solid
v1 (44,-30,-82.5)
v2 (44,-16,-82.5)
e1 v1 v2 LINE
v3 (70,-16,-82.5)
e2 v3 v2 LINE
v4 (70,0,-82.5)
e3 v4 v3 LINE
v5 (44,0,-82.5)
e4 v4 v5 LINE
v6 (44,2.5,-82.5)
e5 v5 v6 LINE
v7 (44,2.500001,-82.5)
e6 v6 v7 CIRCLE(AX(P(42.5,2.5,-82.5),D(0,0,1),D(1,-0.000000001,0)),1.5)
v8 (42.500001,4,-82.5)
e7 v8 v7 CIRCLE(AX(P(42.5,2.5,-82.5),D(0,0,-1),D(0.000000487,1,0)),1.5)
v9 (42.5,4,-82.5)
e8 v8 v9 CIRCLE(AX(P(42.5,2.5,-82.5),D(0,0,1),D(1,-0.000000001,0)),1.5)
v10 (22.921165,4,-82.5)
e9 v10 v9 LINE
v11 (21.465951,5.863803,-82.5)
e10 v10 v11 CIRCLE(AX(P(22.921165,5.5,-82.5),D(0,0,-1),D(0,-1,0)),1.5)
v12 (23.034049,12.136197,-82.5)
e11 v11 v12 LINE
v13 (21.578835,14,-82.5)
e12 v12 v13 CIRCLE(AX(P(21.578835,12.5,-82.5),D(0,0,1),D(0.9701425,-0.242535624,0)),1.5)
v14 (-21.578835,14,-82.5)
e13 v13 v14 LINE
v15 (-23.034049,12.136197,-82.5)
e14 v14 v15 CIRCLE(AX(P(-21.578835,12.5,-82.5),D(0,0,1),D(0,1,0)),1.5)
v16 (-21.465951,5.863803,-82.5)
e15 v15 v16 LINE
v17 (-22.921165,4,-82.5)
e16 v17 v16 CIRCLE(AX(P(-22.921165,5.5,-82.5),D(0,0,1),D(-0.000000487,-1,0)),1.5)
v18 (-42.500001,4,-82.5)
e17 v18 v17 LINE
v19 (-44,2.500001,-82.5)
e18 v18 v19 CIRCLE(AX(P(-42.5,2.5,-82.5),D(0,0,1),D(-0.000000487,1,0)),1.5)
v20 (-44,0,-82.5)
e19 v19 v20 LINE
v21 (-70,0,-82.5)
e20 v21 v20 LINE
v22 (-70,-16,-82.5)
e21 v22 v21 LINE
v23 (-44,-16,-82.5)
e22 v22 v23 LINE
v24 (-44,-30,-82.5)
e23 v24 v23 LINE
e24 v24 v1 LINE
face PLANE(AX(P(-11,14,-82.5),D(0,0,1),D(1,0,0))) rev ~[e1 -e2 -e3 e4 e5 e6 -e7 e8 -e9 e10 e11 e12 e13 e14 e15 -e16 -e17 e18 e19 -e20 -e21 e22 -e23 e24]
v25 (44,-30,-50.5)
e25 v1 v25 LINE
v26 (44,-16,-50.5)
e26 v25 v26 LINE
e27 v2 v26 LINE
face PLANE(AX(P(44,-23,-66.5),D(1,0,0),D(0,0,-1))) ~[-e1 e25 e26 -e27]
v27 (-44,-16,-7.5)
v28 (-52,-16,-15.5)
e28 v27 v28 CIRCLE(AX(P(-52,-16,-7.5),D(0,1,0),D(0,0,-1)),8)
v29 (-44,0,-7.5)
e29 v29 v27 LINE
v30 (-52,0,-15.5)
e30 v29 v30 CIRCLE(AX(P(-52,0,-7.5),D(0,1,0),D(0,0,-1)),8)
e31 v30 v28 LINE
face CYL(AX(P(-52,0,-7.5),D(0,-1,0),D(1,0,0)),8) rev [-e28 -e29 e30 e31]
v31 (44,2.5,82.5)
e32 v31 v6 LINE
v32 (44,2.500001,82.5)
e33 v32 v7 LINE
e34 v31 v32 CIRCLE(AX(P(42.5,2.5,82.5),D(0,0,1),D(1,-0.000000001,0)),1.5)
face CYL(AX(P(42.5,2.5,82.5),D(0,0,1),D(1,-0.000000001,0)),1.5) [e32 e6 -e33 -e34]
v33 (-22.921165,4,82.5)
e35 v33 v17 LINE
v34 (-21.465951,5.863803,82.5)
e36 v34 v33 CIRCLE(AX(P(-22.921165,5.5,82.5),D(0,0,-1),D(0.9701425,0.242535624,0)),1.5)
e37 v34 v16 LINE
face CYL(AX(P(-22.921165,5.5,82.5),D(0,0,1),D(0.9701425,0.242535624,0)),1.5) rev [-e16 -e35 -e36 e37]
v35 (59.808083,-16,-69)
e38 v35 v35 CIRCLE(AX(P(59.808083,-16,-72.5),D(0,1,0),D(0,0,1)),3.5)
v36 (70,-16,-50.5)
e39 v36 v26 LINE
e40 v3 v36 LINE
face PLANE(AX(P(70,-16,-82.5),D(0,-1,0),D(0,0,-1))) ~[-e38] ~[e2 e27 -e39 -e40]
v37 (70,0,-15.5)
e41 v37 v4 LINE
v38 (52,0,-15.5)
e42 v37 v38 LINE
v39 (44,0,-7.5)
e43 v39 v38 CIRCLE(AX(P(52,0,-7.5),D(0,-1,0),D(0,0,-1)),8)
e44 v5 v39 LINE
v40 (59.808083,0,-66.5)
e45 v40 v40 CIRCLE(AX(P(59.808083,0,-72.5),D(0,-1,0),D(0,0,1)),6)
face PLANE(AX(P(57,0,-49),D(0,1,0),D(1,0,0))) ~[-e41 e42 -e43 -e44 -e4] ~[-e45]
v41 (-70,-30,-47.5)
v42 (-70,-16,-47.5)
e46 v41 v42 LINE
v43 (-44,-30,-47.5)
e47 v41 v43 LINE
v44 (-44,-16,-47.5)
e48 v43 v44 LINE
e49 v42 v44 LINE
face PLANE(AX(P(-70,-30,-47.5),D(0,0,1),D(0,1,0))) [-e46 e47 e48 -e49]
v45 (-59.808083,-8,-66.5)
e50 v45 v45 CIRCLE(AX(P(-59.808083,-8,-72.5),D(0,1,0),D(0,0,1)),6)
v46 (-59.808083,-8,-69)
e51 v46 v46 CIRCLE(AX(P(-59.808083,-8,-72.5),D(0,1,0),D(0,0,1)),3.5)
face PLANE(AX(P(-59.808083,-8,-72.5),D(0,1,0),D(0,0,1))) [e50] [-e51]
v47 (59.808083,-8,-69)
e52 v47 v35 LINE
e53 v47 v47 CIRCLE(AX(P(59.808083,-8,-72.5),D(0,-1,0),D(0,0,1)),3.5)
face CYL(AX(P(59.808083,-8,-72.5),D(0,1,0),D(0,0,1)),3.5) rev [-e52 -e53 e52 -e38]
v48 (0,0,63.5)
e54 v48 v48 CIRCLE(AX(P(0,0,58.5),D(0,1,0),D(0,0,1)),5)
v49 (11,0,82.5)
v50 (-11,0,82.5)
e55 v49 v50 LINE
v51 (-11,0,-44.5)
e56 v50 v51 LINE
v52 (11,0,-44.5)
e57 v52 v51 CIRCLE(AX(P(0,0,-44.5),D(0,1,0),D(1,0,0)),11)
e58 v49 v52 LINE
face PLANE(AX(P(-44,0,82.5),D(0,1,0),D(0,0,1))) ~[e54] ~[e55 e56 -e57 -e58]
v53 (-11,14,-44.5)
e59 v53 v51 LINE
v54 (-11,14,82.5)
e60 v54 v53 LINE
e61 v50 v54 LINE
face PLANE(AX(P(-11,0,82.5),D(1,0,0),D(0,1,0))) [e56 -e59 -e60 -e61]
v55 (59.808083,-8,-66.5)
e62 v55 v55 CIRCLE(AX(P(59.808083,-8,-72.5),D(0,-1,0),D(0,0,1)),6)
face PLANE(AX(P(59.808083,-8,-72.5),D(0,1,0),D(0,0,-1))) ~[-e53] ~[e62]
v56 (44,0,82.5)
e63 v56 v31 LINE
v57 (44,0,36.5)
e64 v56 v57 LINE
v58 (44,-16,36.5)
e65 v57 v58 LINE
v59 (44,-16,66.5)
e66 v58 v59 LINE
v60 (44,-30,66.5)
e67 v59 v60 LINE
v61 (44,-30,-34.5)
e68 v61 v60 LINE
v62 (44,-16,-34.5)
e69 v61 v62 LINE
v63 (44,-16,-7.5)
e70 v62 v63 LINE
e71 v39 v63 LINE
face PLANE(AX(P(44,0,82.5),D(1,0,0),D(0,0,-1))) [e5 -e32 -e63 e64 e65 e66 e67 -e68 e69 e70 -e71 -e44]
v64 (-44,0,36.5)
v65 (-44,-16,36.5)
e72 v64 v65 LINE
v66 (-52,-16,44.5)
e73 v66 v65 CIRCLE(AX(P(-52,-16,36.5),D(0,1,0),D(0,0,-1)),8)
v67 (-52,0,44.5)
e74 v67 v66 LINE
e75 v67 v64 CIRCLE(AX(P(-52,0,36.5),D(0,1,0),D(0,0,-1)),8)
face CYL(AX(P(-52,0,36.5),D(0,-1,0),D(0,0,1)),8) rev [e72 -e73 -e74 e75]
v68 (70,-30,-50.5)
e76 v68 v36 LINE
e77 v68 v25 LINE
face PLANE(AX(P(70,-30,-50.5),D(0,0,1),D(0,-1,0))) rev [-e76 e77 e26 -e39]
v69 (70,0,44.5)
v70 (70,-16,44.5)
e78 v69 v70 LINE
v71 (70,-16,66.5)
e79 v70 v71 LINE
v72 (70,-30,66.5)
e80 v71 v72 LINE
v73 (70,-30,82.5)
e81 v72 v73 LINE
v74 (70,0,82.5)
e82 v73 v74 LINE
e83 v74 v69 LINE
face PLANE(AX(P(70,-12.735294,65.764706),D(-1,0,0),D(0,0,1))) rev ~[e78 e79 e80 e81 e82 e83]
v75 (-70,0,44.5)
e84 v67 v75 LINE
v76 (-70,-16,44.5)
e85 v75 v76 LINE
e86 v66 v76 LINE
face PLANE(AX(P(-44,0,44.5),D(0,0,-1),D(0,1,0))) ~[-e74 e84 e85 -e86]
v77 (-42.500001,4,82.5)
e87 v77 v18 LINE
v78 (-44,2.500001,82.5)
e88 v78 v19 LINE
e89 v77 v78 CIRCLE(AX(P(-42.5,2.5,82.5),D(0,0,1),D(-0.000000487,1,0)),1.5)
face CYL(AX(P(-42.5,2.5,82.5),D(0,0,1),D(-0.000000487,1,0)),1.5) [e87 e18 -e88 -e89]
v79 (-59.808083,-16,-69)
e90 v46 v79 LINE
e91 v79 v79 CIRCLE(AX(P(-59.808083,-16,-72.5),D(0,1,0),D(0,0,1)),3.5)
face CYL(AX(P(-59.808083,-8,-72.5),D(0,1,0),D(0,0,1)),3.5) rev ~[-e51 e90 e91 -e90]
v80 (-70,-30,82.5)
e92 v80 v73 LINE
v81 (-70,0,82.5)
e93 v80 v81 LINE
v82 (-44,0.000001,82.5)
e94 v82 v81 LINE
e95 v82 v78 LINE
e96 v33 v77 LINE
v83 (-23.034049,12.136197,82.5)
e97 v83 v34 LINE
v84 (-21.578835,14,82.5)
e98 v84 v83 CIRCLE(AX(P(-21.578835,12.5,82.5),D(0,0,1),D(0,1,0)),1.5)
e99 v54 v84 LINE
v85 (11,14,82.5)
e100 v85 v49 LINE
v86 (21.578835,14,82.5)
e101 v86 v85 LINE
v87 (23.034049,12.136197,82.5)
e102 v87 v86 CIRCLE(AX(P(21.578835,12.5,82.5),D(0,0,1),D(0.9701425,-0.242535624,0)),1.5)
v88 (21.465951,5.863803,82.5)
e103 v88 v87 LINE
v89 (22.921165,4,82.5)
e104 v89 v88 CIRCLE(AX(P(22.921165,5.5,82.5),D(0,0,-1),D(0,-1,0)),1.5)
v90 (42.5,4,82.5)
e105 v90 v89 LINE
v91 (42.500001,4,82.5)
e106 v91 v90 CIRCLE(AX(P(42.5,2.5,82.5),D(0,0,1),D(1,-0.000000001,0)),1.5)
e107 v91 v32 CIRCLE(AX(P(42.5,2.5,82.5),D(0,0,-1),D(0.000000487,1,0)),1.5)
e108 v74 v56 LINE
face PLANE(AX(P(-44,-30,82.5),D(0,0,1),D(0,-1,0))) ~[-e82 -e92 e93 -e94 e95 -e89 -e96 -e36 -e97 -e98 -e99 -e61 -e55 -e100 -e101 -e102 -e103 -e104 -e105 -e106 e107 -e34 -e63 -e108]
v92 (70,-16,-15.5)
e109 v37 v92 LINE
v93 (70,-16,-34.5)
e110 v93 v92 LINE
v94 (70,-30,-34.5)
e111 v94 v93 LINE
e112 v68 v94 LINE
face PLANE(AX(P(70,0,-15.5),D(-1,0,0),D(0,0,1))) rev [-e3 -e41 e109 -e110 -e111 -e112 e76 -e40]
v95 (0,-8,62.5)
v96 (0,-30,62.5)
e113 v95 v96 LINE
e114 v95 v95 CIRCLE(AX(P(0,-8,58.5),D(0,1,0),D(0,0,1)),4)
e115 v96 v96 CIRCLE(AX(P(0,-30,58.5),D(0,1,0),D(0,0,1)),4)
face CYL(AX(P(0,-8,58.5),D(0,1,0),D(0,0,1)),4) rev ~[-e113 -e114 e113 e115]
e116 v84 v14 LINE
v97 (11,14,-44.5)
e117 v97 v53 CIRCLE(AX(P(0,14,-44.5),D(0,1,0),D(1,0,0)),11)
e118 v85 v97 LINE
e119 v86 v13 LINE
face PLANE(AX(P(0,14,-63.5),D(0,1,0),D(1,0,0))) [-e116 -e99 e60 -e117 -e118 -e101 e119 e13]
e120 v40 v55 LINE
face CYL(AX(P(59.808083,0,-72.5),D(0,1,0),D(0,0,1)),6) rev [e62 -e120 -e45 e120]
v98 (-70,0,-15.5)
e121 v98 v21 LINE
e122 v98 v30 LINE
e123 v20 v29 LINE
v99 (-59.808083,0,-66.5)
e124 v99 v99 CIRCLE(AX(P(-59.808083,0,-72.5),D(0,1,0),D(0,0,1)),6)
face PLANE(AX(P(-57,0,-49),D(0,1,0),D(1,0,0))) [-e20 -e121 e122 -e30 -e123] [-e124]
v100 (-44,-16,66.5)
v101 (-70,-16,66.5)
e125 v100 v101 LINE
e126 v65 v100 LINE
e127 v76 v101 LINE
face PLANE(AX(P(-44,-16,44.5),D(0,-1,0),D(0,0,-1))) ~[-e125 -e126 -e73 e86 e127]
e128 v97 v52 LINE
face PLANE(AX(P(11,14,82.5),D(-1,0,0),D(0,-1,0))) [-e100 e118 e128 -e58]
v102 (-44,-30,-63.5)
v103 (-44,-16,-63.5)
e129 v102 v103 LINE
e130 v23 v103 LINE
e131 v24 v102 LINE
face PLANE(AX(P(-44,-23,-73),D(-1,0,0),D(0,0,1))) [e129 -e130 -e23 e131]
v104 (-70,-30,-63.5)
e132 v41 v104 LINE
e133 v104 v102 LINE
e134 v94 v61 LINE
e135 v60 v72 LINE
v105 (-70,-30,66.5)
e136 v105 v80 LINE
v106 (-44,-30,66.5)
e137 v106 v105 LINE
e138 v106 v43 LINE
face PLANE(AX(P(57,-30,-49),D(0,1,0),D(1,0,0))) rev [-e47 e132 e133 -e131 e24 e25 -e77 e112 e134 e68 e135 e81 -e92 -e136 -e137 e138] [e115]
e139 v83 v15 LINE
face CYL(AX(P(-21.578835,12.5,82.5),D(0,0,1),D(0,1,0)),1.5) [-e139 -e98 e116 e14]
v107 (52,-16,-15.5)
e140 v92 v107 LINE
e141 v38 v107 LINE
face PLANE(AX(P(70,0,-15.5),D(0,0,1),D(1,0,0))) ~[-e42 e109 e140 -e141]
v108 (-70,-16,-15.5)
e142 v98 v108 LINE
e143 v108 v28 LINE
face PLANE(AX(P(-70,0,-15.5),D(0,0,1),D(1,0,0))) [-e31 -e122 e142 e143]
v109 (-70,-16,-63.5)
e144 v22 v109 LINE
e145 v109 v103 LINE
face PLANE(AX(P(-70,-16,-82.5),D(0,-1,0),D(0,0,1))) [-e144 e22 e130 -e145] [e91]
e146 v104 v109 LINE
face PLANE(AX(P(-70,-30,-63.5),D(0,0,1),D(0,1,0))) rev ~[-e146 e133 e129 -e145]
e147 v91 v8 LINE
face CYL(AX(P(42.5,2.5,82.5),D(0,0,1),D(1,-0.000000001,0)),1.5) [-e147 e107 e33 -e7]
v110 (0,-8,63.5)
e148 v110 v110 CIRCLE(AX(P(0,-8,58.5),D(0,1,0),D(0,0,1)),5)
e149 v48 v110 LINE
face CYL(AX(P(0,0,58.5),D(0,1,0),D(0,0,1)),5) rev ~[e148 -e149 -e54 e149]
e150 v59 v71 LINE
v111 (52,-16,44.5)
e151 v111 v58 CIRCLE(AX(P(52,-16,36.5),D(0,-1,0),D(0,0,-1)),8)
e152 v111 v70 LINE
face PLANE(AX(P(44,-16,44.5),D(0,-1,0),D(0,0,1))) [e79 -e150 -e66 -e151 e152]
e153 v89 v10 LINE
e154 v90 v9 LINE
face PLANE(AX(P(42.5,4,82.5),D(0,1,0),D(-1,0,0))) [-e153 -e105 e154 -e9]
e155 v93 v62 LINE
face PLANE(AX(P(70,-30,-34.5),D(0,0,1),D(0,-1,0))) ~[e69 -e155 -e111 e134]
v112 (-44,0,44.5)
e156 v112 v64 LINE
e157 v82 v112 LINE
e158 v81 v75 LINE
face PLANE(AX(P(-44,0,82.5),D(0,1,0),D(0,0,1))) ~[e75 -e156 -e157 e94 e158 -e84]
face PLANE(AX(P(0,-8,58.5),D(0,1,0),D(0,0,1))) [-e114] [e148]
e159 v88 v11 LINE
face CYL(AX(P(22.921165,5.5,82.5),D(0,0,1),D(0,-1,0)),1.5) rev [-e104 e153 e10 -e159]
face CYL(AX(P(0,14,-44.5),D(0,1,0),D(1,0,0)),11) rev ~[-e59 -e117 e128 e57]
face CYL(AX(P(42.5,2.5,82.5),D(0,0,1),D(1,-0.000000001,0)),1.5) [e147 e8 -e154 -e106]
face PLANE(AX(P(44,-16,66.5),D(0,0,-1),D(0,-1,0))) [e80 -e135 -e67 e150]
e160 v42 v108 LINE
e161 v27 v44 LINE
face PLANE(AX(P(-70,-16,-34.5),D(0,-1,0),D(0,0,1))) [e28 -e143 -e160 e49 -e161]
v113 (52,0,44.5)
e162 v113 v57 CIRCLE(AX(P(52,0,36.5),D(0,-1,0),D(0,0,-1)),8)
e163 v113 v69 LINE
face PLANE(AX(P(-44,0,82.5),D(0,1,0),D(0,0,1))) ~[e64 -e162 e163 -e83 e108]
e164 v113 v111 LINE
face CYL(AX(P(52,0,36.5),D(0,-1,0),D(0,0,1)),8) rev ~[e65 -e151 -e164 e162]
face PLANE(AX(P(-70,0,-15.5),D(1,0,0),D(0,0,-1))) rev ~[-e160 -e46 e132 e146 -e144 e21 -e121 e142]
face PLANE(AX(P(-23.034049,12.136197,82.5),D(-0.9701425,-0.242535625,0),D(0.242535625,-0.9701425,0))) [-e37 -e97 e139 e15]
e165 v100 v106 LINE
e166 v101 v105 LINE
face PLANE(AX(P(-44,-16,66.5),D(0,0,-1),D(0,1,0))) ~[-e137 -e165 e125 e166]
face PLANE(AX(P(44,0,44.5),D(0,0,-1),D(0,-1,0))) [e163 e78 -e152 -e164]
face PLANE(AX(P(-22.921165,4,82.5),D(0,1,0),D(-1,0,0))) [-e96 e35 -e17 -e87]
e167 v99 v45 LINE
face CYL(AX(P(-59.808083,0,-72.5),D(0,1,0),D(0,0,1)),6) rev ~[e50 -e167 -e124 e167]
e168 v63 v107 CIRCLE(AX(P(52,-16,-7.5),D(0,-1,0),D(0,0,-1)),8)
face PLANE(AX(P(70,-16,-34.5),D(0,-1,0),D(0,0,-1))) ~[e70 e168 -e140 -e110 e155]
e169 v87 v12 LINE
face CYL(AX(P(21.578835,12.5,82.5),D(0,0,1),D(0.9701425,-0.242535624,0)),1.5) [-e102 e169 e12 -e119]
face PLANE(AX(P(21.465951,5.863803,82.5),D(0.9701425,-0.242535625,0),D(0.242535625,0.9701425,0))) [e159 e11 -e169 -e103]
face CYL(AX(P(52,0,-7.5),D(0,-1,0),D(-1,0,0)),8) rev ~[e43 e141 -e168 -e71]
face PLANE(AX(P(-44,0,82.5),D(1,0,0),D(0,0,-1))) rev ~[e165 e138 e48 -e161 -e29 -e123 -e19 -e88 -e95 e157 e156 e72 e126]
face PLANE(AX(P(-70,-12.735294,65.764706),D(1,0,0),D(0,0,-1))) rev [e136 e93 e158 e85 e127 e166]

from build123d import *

# Parameters (mm, degrees)
BASE_PLATE_DEPTH            = 30
SIDE_LUG_DEPTH              = 26
GUIDE_RAIL_PROFILE_DEPTH    = 165
END_BLOCK_SKETCH_W          = 26
END_BLOCK_SKETCH_H          = 67
END_BLOCK_DEPTH             = 30
END_NOTCH_SKETCH_W          = 19
END_NOTCH_SKETCH_H          = 14
END_NOTCH_SKETCH_W_2        = 32
END_NOTCH_CUT_DEPTH         = 26
NOTCH_FILLET_R1_5_A_R       = 1.5
NOTCH_FILLET_R1_5_B_R       = 1.5
MOUNTING_HOLE_SKETCH_R      = 6
MOUNTING_HOLE_DEPTH_8_DEPTH = 8
THROUGH_HOLE_SKETCH_R       = 3.5
THROUGH_HOLE_DEPTH_32_DEPTH = 32
END_BLOCK_FILLET_R8_R       = 8
SIDE_LUG_FILLET_R8_R        = 8
LONG_BORE_A_SKETCH_R        = 3.5
LONG_BORE_A_DEPTH_96_DEPTH  = 96
LONG_BORE_B_SKETCH_R        = 3.53
LONG_BORE_B_DEPTH_96_DEPTH  = 96
CENTRE_BOSS_SKETCH_W        = 22
CENTRE_BOSS_SKETCH_H        = 38
CENTRE_BOSS_DEPTH           = 14
CENTRE_SLOT_CUT_DEPTH       = 14
COUNTERBORE_10_SKETCH_R     = 5
COUNTERBORE_10_DEPTH        = 8
DEEP_BORE_SKETCH_R          = 4
DEEP_BORE_DEPTH_65_DEPTH    = 65
SECOND_END_NOTCH_SKETCH_W   = 32
SECOND_END_NOTCH_SKETCH_H   = 14
SECOND_END_NOTCH_SKETCH_W_2 = 19
SECOND_END_NOTCH_CUT_DEPTH  = 26


with BuildPart() as part:
    # Base Plate Sketch → Base Plate (new body)
    with BuildSketch(Plane(origin=(0, 0, 0), x_dir=(1, 0, 0), z_dir=(0, 1, 0))):
        Polygon((44, 0), (44, -82.5), (-44, -82.5), (-44, 82.5), (44, 82.5), align=None)
    extrude(amount=-BASE_PLATE_DEPTH)

    # Side Lug Sketch → Side Lug (add)
    with BuildSketch(Plane(origin=(44, 0, 0), x_dir=(0, 0, -1), z_dir=(1, 0, 0))):
        Polygon((-82.5, -30), (-82.5, 0), (-44.5, 0), (-44.5, -16), (-66.5, -16), (-66.5, -30), align=None)
    side_lug = extrude(amount=SIDE_LUG_DEPTH)

    # Side Lug Mirror: Side Lug across plane
    add(side_lug.mirror(Plane(origin=(0, 0, 0), x_dir=(0, 0, 1), z_dir=(1, 0, 0))))


with BuildPart() as guide_rail_profile_tool:
    # Guide Rail Profile Sketch → Guide Rail Profile (new body)
    with BuildSketch(Plane.XY.offset(82.5)):
        with BuildLine():
            Line((11, 14), (11, 0))
            Line((11, 0), (44, 0))
            Line((44, 0), (44, 2.5))
            ThreePointArc((44, 2.5), (43.560660172, 3.560660172), (42.5, 4))
            Line((42.5, 4), (22.92116461, 4))
            ThreePointArc((22.92116461, 4), (21.738856453, 4.576881686), (21.465950859, 5.863803438))
            Line((21.465950859, 5.863803438), (23.034049141, 12.136196562))
            ThreePointArc((23.034049141, 12.136196562), (22.761143547, 13.423118314), (21.57883539, 14))
            Line((21.57883539, 14), (11, 14))
        make_face()
        with BuildLine():
            Line((-44, 7.32e-07), (-11, 0))
            Line((-11, 0), (-11, 14))
            Line((-11, 14), (-21.57883539, 14))
            ThreePointArc((-21.57883539, 14), (-22.761143547, 13.423118314), (-23.034049141, 12.136196562))
            Line((-23.034049141, 12.136196562), (-21.465950859, 5.863803438))
            ThreePointArc((-21.465950859, 5.863803438), (-21.738856678, 4.576881398), (-22.921165341, 4))
            Line((-22.921165341, 4), (-42.500000732, 4))
            ThreePointArc((-42.500000732, 4), (-43.560660172, 3.560660172), (-44, 2.500000732))
            Line((-44, 2.500000732), (-44, 7.32e-07))
        make_face()
    extrude(amount=-GUIDE_RAIL_PROFILE_DEPTH)


with BuildPart() as part_1:
    add(part.part)


with BuildPart() as part_2:
    # Guide Rail Profile: joined with guide_rail_profile_tool
    add(part_1.part.fuse(guide_rail_profile_tool.part, tol=0.00001))

    # End Block Sketch → End Block (add)
    with BuildSketch(Plane(origin=(0, 0, 0), x_dir=(1, 0, 0), z_dir=(0, 1, 0))):
        with Locations((-57, 49)):
            Rectangle(END_BLOCK_SKETCH_W, END_BLOCK_SKETCH_H)
    end_block = extrude(amount=-END_BLOCK_DEPTH)

    # End Notch Sketch → End Notch Cut (cut)
    with BuildSketch(Plane.ZY.offset(70)):
        with Locations((-25, -23)):
            Rectangle(END_NOTCH_SKETCH_W, END_NOTCH_SKETCH_H)
        with Locations((-66.5, -23)):
            Rectangle(END_NOTCH_SKETCH_W_2, END_NOTCH_SKETCH_H)
    end_notch_cut = extrude(amount=-END_NOTCH_CUT_DEPTH, mode=Mode.SUBTRACT)

    # Notch Fillet R1.5 A
    notch_fillet_r1_5_a_edges = [part_2.edges().sort_by_distance(p)[0] for p in [
        (-57, -16, -50.5),
    ]]
    fillet(notch_fillet_r1_5_a_edges, radius=NOTCH_FILLET_R1_5_A_R)

    # Notch Fillet R1.5 B
    notch_fillet_r1_5_b_edges = [part_2.edges().sort_by_distance(p)[0] for p in [
        (-57, -16, -34.5),
    ]]
    fillet(notch_fillet_r1_5_b_edges, radius=NOTCH_FILLET_R1_5_B_R)

    # Mounting Hole Sketch → Mounting Hole Depth 8 (cut)
    with BuildSketch(Plane(origin=(0, 0, 0), x_dir=(1, 0, 0), z_dir=(0, 1, 0))):
        with Locations(Location((-59.808082778, 72.5, 0), (0, 0, 270))):
            Circle(MOUNTING_HOLE_SKETCH_R)
    mounting_hole_depth_8 = extrude(amount=-MOUNTING_HOLE_DEPTH_8_DEPTH, mode=Mode.SUBTRACT)

    # Through Hole Sketch → Through Hole Depth 32 (cut)
    with BuildSketch(Plane(origin=(0, 0, 0), x_dir=(1, 0, 0), z_dir=(0, 1, 0))):
        with Locations(Location((-59.808082778, 72.5, 0), (0, 0, 270))):
            Circle(THROUGH_HOLE_SKETCH_R)
    extrude(amount=-THROUGH_HOLE_DEPTH_32_DEPTH, mode=Mode.SUBTRACT)

    # Mounting Hole Mirror: End Block, Mounting Hole Depth 8 across plane
    add(end_block.mirror(Plane(origin=(0, 0, 0), x_dir=(0, 0, 1), z_dir=(1, 0, 0))))
    add(mounting_hole_depth_8.mirror(Plane(origin=(0, 0, 0), x_dir=(0, 0, 1), z_dir=(1, 0, 0))), mode=Mode.SUBTRACT)

    # End Block Fillet R8
    end_block_fillet_r8_edges = [part_2.edges().sort_by_distance(p)[0] for p in [
        (-44, -8, -15.5),
    ]]
    fillet(end_block_fillet_r8_edges, radius=END_BLOCK_FILLET_R8_R)

    # Side Lug Fillet R8
    side_lug_fillet_r8_edges = [part_2.edges().sort_by_distance(p)[0] for p in [
        (-44, -8, 44.5),
    ]]
    fillet(side_lug_fillet_r8_edges, radius=SIDE_LUG_FILLET_R8_R)

    # Body Mirror: part across plane


with BuildPart() as part_3:
    add(part_2.part)
    add(part_2.part.mirror(Plane(origin=(0, 0, 0), x_dir=(0, 0, 1), z_dir=(1, 0, 0))))

    # Long Bore A Sketch → Long Bore A Depth 96 (cut)
    with BuildSketch(Plane(origin=(0, -8, 0), x_dir=(1, 0, 0), z_dir=(0, 1, 0))):
        with Locations(Location((-59.808082778, 72.5, 0), (0, 0, 270))):
            Circle(LONG_BORE_A_SKETCH_R)
    long_bore_a_depth_96 = extrude(amount=-LONG_BORE_A_DEPTH_96_DEPTH, mode=Mode.SUBTRACT)

    # Long Bore B Sketch → Long Bore B Depth 96 (cut)
    with BuildSketch(Plane.XZ.offset(30)):
        with Locations(Location((59.808082778, -72.5, 0), (0, 0, 270))):
            Circle(LONG_BORE_B_SKETCH_R)
    extrude(amount=-LONG_BORE_B_DEPTH_96_DEPTH, mode=Mode.SUBTRACT)

    # Centre Boss Sketch → Centre Boss (add)
    with BuildSketch(Plane(origin=(0, 14, 0), x_dir=(1, 0, 0), z_dir=(0, 1, 0))):
        with Locations((0, 63.5)):
            Rectangle(CENTRE_BOSS_SKETCH_W, CENTRE_BOSS_SKETCH_H)
    extrude(amount=-CENTRE_BOSS_DEPTH)

    # Centre Slot Sketch → Centre Slot Cut (cut)
    with BuildSketch(Plane(origin=(0, 14, 0), x_dir=(1, 0, 0), z_dir=(0, 1, 0))):
        with BuildLine():
            Line((-11, 44.5), (11, 44.5))
            ThreePointArc((11, 44.5), (0, 55.5), (-11, 44.5))
        make_face()
    extrude(amount=-CENTRE_SLOT_CUT_DEPTH, mode=Mode.SUBTRACT)

    # Counterbore Ø10 Sketch → Counterbore Ø10 (cut)
    with BuildSketch(Plane(origin=(0, 0, 0), x_dir=(1, 0, 0), z_dir=(0, 1, 0))):
        with Locations(Location((0, -58.5, 0), (0, 0, 270))):
            Circle(COUNTERBORE_10_SKETCH_R)
    extrude(amount=-COUNTERBORE_10_DEPTH, mode=Mode.SUBTRACT)

    # Deep Bore Sketch → Deep Bore Depth 65 (cut)
    with BuildSketch(Plane(origin=(0, -8, 0), x_dir=(1, 0, 0), z_dir=(0, 1, 0))):
        with Locations(Location((0, -58.5, 0), (0, 0, 270))):
            Circle(DEEP_BORE_SKETCH_R)
    extrude(amount=-DEEP_BORE_DEPTH_65_DEPTH, mode=Mode.SUBTRACT)

    # Second End Notch Sketch → Second End Notch Cut (cut)
    with BuildSketch(Plane.ZY.offset(70)):
        with Locations((-31.5, -23)):
            Rectangle(SECOND_END_NOTCH_SKETCH_W, SECOND_END_NOTCH_SKETCH_H)
        with Locations((-73, -23)):
            Rectangle(SECOND_END_NOTCH_SKETCH_W_2, SECOND_END_NOTCH_SKETCH_H)
    extrude(amount=-SECOND_END_NOTCH_CUT_DEPTH, mode=Mode.SUBTRACT)

    # End Notch Mirror: End Block, End Notch Cut across plane
    add(end_block.mirror(Plane(origin=(0, 0, 0), x_dir=(0, 0, 1), z_dir=(1, 0, 0))))
    add(end_notch_cut.mirror(Plane(origin=(0, 0, 0), x_dir=(0, 0, 1), z_dir=(1, 0, 0))), mode=Mode.SUBTRACT)

    # Mounting Hole Mirror 2: Mounting Hole Depth 8 across plane
    add(mounting_hole_depth_8.mirror(Plane(origin=(0, 0, 0), x_dir=(0, 0, 1), z_dir=(1, 0, 0))), mode=Mode.SUBTRACT)

    # Long Bore Mirror: Long Bore A Depth 96 across plane
    add(long_bore_a_depth_96.mirror(Plane(origin=(0, 0, 0), x_dir=(0, 0, 1), z_dir=(1, 0, 0))), mode=Mode.SUBTRACT)


solid = part_3.part
